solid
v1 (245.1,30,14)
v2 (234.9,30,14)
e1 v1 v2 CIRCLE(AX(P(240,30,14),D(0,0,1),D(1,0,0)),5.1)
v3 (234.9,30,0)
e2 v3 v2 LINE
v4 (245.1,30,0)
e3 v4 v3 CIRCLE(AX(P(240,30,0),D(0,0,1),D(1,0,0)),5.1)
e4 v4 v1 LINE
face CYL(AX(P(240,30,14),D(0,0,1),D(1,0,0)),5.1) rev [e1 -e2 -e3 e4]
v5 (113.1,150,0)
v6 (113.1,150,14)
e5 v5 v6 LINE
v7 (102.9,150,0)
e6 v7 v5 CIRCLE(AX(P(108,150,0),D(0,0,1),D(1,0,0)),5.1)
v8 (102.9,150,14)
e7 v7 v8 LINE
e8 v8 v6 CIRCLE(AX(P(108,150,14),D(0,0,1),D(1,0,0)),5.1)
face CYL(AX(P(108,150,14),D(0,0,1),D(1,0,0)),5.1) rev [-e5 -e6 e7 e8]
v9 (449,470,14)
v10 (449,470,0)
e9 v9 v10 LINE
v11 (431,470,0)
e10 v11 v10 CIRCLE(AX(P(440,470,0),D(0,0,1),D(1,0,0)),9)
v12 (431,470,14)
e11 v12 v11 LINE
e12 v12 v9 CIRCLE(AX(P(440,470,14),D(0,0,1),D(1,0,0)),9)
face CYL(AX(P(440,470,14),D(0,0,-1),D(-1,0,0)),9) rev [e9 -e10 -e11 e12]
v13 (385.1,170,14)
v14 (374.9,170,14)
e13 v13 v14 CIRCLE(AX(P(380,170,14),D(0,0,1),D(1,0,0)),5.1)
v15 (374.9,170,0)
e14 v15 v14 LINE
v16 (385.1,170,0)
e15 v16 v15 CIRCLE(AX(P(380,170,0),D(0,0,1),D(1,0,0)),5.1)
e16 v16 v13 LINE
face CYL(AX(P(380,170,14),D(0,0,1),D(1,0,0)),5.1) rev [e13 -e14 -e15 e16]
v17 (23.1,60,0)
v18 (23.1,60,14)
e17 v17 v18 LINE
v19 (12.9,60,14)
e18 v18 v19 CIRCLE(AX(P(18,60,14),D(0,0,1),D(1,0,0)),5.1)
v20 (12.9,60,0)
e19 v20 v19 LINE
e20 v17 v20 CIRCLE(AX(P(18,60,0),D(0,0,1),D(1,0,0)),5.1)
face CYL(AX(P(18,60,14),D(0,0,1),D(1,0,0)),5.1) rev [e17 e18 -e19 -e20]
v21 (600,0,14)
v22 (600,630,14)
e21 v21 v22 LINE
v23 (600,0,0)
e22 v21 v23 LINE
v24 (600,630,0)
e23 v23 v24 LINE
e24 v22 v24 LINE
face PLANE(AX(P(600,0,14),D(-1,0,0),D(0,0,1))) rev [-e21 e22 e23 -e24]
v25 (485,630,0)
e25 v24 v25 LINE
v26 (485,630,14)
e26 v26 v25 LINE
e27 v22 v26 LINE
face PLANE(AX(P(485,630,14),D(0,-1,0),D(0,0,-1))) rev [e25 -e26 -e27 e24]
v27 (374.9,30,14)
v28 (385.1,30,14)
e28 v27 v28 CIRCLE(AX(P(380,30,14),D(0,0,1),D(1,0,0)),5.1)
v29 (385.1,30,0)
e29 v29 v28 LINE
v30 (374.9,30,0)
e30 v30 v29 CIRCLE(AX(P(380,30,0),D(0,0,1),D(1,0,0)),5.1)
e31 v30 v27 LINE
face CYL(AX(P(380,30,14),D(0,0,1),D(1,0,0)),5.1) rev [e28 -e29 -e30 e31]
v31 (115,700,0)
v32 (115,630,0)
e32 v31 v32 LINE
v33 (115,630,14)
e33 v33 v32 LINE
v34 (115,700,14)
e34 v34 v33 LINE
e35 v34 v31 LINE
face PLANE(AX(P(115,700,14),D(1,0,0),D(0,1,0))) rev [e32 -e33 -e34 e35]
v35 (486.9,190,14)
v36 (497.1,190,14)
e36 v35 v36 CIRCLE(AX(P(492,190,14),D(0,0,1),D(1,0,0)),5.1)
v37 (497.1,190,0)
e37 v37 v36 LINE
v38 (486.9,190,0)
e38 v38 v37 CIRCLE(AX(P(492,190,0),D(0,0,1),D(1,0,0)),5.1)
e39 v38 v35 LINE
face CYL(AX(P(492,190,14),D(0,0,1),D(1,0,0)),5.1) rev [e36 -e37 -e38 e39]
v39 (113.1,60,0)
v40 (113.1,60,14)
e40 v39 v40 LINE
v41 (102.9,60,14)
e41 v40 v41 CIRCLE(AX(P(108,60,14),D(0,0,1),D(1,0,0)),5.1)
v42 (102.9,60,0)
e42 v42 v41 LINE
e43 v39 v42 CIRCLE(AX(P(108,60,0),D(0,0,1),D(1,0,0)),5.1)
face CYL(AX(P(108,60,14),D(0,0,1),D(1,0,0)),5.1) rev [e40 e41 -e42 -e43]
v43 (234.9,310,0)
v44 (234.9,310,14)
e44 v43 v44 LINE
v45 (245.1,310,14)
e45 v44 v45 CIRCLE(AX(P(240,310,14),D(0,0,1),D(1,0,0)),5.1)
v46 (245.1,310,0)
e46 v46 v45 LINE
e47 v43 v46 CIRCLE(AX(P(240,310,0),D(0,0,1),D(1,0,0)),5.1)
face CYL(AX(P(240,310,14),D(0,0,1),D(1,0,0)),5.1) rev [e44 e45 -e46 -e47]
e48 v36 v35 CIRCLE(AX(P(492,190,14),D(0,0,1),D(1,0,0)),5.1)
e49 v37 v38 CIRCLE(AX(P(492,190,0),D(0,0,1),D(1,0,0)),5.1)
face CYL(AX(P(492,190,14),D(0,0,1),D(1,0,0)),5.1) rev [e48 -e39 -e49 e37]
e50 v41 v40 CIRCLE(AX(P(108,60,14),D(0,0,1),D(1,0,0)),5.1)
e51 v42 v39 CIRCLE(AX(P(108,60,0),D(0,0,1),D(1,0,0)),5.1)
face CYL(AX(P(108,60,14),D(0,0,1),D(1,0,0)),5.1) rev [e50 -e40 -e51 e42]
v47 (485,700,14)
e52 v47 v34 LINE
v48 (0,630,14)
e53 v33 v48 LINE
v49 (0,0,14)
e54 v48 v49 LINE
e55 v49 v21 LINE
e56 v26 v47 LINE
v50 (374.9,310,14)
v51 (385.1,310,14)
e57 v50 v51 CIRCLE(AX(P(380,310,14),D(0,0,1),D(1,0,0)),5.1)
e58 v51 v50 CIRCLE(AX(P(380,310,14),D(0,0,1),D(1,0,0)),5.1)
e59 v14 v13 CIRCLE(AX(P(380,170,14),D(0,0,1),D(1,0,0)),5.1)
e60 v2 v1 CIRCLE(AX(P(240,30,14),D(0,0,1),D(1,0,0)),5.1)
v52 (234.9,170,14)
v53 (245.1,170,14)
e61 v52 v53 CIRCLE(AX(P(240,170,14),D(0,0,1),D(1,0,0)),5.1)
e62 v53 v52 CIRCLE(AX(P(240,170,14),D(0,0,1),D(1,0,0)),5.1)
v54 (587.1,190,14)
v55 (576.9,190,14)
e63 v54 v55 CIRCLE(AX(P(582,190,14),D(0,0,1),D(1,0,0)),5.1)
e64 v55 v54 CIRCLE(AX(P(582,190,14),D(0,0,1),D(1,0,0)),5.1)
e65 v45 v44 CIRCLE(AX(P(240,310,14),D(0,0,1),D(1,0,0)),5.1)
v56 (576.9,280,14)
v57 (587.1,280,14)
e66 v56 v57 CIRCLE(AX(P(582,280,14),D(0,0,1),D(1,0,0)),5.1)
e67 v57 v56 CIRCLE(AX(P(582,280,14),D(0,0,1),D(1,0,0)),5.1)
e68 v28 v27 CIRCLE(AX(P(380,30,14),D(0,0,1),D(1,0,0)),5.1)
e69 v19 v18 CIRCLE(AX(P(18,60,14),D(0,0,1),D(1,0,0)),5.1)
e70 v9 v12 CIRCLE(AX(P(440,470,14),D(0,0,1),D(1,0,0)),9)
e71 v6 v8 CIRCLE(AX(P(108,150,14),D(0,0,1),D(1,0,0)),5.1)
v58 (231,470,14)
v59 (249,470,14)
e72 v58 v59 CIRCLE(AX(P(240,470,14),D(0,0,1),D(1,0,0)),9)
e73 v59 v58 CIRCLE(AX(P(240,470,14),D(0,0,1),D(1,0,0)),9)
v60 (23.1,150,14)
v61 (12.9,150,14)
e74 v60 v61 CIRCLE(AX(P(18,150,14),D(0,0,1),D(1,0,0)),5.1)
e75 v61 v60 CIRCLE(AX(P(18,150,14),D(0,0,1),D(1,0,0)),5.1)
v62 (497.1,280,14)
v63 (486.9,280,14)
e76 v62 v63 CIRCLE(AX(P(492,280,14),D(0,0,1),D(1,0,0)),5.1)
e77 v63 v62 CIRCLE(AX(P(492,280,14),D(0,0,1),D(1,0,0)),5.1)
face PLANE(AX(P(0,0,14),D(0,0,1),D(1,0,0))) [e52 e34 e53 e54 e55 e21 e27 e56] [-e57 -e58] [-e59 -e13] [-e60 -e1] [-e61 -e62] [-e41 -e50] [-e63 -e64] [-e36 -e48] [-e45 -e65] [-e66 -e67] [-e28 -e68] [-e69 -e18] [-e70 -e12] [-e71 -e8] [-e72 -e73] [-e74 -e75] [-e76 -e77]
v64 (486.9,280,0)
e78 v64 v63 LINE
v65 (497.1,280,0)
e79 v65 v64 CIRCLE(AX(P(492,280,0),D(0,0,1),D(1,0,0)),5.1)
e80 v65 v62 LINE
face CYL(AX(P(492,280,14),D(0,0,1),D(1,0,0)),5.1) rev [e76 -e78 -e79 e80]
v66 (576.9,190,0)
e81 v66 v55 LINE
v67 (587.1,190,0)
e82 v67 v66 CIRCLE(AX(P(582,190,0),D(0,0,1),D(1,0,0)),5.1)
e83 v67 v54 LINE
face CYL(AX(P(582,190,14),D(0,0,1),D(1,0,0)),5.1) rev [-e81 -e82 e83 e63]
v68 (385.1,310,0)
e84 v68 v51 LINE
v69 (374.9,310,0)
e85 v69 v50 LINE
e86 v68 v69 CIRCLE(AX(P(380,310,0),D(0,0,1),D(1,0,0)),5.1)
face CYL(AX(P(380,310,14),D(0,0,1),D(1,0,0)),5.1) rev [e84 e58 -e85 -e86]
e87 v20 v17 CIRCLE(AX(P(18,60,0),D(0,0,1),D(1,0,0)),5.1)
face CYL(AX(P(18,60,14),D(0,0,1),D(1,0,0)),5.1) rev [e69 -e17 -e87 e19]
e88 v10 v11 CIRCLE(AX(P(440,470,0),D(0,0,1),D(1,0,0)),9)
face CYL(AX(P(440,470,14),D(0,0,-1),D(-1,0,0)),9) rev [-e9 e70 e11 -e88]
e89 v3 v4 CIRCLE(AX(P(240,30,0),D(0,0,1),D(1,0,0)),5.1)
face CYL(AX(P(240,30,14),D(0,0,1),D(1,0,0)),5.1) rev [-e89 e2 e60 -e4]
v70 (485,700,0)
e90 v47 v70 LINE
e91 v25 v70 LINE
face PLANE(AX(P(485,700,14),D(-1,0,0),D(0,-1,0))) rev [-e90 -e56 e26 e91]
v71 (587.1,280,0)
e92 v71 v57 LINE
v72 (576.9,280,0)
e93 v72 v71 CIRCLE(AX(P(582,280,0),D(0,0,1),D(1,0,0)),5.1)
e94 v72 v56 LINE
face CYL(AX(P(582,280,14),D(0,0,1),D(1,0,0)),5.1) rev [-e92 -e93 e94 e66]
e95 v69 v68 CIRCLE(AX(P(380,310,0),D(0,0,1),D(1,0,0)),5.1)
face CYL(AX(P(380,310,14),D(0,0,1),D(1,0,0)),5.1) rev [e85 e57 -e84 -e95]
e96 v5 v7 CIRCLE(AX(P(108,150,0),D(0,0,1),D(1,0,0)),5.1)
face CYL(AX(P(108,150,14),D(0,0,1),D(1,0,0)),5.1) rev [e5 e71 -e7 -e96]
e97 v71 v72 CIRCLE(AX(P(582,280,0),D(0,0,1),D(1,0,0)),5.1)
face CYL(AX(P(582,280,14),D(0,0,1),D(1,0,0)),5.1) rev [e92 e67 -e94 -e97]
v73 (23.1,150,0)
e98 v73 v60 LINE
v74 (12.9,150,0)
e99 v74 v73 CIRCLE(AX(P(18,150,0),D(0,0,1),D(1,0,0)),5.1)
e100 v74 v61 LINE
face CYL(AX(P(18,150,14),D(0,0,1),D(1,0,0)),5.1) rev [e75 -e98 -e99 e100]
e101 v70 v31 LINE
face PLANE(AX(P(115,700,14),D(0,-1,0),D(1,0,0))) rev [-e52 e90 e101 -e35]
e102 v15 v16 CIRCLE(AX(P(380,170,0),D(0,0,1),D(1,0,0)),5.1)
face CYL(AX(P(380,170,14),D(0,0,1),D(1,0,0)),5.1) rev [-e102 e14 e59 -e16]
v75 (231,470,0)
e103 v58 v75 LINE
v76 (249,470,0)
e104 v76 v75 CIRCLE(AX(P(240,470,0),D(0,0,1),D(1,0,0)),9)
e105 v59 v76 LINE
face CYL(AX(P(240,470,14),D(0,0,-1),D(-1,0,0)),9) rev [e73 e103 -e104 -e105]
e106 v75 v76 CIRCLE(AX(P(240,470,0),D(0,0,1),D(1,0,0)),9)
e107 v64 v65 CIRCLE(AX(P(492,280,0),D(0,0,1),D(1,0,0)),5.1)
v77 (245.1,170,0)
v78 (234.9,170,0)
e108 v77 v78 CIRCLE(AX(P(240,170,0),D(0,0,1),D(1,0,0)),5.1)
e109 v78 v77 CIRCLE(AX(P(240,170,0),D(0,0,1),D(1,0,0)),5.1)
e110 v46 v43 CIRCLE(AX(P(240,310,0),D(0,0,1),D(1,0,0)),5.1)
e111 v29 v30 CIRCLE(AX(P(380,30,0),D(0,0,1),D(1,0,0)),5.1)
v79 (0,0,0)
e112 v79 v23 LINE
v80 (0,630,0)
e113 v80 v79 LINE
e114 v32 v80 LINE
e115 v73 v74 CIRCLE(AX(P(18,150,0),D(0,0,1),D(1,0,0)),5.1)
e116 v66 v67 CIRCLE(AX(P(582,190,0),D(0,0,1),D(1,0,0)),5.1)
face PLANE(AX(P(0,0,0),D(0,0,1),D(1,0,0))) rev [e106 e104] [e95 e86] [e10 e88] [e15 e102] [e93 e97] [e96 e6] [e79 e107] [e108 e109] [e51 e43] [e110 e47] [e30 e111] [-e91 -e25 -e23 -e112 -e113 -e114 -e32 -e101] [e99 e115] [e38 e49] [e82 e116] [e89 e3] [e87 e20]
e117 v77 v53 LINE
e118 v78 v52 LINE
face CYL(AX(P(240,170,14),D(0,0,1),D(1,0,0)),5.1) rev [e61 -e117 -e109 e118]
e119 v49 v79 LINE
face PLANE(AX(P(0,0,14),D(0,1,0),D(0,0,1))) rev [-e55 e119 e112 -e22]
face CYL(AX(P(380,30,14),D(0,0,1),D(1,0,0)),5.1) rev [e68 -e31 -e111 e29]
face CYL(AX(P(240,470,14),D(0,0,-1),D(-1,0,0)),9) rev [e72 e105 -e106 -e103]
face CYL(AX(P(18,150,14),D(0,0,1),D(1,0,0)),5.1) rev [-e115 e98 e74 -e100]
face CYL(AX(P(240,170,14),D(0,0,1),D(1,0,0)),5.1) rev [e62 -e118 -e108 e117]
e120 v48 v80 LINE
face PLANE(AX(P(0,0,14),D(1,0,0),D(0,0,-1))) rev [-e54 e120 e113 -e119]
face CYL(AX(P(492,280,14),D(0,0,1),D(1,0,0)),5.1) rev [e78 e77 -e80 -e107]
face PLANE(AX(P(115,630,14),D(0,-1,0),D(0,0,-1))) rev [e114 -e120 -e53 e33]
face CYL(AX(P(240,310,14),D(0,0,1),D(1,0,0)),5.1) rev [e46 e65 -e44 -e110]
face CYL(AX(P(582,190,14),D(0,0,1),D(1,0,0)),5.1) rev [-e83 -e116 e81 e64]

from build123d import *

# Parameters (mm, degrees)
SKETCH_1_R          = 9
EXTRUDE_1_DEPTH     = 14
HOLE_WIZARD_M12_1_D = 10.2


with BuildPart() as part:
    # 草图1 → 凸台-拉伸1 (new body)
    with BuildSketch(Plane.XY):
        Polygon((115, 700), (115, 630), (0, 630), (0, 0), (600, 0), (600, 630), (485, 630), (485, 700), align=None)
        with Locations((440, 470)):
            Circle(SKETCH_1_R, mode=Mode.SUBTRACT)
        with Locations((240, 470)):
            Circle(SKETCH_1_R, mode=Mode.SUBTRACT)
    extrude(amount=EXTRUDE_1_DEPTH)

    # M12 螺纹孔1 (through all)
    with Locations(Plane(origin=(18, 150, 14), x_dir=(1, 0, 0), z_dir=(0, 0, 1))):
        with Locations((0, 0), (90, 0), (0, -90), (90, -90), (474, 130), (564, 130), (474, 40), (564, 40), (222, 160), (362, 160), (222, 20), (362, 20), (222, -120), (362, -120)):
            Hole(HOLE_WIZARD_M12_1_D / 2)


solid = part.part
